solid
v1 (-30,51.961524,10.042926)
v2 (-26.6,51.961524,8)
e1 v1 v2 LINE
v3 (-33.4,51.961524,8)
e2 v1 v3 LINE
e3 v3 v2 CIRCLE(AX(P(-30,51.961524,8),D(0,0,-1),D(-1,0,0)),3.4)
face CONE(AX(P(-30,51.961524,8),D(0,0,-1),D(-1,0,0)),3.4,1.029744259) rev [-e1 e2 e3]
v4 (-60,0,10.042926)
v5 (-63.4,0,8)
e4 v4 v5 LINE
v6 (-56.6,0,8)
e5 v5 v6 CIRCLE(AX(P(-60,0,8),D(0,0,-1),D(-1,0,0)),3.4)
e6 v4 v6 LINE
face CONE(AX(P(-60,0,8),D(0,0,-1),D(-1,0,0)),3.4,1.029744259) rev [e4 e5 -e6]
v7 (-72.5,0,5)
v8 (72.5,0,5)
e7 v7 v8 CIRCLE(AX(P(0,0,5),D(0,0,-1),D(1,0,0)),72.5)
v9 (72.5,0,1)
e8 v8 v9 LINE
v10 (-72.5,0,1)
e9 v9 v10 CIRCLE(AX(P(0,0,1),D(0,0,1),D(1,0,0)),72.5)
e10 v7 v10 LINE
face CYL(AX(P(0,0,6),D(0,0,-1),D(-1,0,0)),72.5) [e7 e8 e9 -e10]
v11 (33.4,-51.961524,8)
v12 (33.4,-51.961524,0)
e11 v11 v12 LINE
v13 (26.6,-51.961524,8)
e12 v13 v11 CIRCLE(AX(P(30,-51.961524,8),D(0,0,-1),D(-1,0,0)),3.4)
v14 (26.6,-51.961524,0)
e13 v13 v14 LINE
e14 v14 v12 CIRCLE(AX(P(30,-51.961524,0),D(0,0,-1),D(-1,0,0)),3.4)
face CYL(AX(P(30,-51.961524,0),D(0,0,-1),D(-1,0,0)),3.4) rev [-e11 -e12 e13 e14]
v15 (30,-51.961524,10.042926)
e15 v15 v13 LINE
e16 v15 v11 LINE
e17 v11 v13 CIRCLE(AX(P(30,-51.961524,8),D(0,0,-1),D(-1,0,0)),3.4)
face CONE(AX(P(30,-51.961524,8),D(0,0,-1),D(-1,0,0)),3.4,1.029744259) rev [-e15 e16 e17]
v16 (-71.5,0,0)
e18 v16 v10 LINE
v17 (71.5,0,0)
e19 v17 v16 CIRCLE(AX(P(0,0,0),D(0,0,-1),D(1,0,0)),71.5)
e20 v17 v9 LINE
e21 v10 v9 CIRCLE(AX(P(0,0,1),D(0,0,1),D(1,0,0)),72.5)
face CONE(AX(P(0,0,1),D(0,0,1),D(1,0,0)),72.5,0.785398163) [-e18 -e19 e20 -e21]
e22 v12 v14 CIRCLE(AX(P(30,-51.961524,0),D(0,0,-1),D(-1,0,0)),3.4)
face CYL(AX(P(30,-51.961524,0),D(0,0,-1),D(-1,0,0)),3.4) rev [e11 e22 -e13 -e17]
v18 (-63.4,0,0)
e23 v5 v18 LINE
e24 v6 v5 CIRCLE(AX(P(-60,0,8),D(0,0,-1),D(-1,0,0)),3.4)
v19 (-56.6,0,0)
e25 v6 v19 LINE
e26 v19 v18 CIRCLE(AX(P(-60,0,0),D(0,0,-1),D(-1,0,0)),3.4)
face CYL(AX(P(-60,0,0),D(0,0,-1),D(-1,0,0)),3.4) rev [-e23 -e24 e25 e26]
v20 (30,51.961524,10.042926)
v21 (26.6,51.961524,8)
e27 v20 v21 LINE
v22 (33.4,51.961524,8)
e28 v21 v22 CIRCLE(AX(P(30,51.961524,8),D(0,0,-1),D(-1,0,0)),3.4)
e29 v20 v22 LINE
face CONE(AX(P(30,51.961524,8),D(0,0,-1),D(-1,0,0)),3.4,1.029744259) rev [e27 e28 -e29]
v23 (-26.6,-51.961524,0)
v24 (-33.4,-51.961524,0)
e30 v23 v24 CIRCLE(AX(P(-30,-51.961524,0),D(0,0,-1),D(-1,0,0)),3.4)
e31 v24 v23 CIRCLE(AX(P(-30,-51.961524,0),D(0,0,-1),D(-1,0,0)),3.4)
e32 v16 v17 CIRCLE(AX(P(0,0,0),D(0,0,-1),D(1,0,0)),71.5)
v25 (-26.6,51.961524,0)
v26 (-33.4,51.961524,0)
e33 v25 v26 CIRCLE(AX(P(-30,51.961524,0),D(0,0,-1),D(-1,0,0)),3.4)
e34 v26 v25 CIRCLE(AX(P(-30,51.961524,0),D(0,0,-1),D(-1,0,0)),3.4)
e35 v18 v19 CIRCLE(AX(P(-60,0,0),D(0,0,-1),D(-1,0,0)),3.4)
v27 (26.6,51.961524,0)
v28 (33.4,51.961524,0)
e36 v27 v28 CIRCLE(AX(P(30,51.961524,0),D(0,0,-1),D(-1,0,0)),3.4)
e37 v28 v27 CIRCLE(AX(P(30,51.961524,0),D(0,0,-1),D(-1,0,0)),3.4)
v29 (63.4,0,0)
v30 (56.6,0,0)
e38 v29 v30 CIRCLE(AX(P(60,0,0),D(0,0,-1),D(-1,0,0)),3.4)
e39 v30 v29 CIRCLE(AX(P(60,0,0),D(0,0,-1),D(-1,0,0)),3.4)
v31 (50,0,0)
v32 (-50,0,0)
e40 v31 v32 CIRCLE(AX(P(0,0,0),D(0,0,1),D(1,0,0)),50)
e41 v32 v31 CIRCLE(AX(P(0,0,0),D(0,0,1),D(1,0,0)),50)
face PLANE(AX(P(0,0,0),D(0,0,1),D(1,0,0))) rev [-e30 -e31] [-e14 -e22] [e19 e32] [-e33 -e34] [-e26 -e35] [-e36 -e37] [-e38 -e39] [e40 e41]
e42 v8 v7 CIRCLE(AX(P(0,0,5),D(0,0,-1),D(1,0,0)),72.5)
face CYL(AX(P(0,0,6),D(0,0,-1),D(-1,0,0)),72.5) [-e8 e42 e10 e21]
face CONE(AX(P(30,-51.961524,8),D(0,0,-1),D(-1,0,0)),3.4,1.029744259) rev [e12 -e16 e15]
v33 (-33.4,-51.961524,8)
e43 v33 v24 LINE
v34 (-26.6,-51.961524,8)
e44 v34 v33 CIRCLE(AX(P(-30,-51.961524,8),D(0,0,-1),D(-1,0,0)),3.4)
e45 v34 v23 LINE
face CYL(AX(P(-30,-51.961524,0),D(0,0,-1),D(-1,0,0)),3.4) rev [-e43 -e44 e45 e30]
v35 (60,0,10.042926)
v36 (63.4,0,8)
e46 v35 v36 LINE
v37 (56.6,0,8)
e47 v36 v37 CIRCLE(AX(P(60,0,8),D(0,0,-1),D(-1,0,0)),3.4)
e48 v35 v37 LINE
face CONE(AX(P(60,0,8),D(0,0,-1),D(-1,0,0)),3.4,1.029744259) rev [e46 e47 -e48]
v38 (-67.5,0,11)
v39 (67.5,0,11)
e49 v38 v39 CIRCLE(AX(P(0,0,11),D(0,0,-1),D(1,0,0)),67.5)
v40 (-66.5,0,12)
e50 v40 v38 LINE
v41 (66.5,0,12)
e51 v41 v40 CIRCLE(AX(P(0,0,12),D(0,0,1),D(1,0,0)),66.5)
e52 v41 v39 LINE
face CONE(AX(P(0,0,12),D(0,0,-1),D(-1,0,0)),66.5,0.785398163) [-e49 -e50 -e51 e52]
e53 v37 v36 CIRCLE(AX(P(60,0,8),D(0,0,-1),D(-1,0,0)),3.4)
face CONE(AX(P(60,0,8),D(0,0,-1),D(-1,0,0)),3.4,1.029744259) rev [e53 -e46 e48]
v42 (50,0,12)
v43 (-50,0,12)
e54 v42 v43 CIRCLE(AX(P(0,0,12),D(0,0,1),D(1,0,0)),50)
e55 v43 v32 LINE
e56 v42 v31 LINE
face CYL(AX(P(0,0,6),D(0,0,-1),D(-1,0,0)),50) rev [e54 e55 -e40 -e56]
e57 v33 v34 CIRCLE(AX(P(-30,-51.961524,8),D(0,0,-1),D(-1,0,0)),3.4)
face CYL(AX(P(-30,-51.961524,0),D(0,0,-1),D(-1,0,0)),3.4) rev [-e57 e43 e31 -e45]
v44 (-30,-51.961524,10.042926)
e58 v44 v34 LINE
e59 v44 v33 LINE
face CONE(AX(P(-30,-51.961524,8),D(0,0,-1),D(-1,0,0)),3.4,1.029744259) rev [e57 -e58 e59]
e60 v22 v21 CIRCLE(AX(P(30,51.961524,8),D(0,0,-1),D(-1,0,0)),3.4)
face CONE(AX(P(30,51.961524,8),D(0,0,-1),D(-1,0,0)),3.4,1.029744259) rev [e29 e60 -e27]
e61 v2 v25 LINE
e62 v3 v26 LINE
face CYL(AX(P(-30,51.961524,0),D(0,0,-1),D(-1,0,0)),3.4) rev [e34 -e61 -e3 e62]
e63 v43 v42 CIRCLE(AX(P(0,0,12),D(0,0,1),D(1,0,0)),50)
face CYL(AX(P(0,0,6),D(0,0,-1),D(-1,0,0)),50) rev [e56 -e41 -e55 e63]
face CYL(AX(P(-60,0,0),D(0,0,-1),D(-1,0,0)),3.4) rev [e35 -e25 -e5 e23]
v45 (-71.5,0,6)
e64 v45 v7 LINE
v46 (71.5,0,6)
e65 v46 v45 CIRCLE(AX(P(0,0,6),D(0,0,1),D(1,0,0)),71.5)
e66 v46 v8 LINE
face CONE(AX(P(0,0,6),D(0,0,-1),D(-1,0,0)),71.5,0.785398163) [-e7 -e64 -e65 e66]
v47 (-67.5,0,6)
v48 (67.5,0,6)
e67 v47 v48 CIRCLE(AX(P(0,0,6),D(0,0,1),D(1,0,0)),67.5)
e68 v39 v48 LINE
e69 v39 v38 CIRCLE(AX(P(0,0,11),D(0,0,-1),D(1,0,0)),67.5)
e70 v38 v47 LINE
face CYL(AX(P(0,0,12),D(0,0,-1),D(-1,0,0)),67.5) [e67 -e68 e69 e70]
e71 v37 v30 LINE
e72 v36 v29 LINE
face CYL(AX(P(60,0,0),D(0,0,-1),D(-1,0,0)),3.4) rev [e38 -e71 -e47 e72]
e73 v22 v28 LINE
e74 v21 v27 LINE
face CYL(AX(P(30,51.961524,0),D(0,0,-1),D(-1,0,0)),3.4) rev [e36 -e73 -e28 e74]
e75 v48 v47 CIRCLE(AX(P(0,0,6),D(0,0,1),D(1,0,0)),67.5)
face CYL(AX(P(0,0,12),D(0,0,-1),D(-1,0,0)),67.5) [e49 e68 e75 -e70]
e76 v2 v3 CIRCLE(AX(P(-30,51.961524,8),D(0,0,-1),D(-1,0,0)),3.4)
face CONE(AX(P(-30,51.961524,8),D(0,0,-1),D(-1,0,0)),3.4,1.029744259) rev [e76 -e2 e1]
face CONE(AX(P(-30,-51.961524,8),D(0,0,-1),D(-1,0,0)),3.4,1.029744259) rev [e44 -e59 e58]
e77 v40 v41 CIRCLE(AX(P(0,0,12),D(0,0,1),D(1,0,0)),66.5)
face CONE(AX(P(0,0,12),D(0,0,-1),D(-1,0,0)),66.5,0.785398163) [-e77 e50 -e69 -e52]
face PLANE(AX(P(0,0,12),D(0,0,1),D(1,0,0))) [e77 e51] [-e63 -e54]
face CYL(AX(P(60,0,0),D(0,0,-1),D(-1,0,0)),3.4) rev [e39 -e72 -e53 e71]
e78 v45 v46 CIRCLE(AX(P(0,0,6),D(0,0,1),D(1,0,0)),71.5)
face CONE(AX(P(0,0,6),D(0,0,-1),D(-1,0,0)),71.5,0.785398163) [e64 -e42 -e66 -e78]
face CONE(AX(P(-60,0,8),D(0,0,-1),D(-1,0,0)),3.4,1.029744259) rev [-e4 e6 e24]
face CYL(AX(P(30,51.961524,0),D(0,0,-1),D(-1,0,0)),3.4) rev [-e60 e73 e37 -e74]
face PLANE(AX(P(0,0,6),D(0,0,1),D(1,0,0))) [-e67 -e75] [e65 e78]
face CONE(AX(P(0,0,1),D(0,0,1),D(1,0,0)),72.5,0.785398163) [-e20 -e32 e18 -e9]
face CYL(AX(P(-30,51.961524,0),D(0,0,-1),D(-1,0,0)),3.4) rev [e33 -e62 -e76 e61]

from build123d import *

# Parameters (mm, degrees)
SKETCH1_R             = 72.5
SKETCH1_R_2           = 50
BOSS_EXTRUDE1_DEPTH   = 6
SKETCH2_R             = 67.5
SKETCH2_R_2           = 50
BOSS_EXTRUDE2_DEPTH   = 6
CHAMFER1_SIZE         = 1
SKETCH3_R             = 3
CUT_EXTRUDE1_DEPTH    = 8
M8_TAPPED_HOLE1_D     = 6.8
M8_TAPPED_HOLE1_DEPTH = 8
M8_TAPPED_HOLE1_TIP   = 2.042926105


with BuildPart() as part:
    # Sketch1 → Boss-Extrude1 (new body)
    with BuildSketch(Plane.XY):
        Circle(SKETCH1_R)
        Circle(SKETCH1_R_2, mode=Mode.SUBTRACT)
    extrude(amount=BOSS_EXTRUDE1_DEPTH)

    # Sketch2 → Boss-Extrude2 (add)
    with BuildSketch(Plane.XY.offset(6)):
        Circle(SKETCH2_R)
        Circle(SKETCH2_R_2, mode=Mode.SUBTRACT)
    extrude(amount=BOSS_EXTRUDE2_DEPTH)

    # Chamfer1
    chamfer1_edges = [part.edges().sort_by_distance(p)[0] for p in [
        (-67.5, 0, 12),
        (-72.5, 0, 0),
        (-72.5, 0, 6),
    ]]
    chamfer(chamfer1_edges, length=CHAMFER1_SIZE)

    # Sketch3 → Cut-Extrude1 (cut)
    with BuildSketch(Plane(origin=(0, 0, 0), x_dir=(-1, 0, 0), z_dir=(0, 0, -1))):
        with Locations((-30, 51.961524227)):
            Circle(SKETCH3_R)
        with Locations((-60, 0)):
            Circle(SKETCH3_R)
        with Locations((30, 51.961524227)):
            Circle(SKETCH3_R)
        with Locations((60, 0)):
            Circle(SKETCH3_R)
        with Locations((30, -51.961524227)):
            Circle(SKETCH3_R)
        with Locations((-30, -51.961524227)):
            Circle(SKETCH3_R)
    extrude(amount=-CUT_EXTRUDE1_DEPTH, mode=Mode.SUBTRACT)

    # M8 Tapped Hole1
    with Locations(Plane(origin=(0, 0, 0), x_dir=(-1, 0, 0), z_dir=(0, 0, -1))):
        with Locations((-30, 51.961524227), (30, 51.961524227), (60, 0), (30, -51.961524227), (-30, -51.961524227), (-60, 0)):
            Hole(M8_TAPPED_HOLE1_D / 2, depth=M8_TAPPED_HOLE1_DEPTH)
            with Locations((0, 0, -(M8_TAPPED_HOLE1_DEPTH + M8_TAPPED_HOLE1_TIP / 2))):  # 118° drill point
                Cone(0, M8_TAPPED_HOLE1_D / 2, M8_TAPPED_HOLE1_TIP, mode=Mode.SUBTRACT)


solid = part.part
